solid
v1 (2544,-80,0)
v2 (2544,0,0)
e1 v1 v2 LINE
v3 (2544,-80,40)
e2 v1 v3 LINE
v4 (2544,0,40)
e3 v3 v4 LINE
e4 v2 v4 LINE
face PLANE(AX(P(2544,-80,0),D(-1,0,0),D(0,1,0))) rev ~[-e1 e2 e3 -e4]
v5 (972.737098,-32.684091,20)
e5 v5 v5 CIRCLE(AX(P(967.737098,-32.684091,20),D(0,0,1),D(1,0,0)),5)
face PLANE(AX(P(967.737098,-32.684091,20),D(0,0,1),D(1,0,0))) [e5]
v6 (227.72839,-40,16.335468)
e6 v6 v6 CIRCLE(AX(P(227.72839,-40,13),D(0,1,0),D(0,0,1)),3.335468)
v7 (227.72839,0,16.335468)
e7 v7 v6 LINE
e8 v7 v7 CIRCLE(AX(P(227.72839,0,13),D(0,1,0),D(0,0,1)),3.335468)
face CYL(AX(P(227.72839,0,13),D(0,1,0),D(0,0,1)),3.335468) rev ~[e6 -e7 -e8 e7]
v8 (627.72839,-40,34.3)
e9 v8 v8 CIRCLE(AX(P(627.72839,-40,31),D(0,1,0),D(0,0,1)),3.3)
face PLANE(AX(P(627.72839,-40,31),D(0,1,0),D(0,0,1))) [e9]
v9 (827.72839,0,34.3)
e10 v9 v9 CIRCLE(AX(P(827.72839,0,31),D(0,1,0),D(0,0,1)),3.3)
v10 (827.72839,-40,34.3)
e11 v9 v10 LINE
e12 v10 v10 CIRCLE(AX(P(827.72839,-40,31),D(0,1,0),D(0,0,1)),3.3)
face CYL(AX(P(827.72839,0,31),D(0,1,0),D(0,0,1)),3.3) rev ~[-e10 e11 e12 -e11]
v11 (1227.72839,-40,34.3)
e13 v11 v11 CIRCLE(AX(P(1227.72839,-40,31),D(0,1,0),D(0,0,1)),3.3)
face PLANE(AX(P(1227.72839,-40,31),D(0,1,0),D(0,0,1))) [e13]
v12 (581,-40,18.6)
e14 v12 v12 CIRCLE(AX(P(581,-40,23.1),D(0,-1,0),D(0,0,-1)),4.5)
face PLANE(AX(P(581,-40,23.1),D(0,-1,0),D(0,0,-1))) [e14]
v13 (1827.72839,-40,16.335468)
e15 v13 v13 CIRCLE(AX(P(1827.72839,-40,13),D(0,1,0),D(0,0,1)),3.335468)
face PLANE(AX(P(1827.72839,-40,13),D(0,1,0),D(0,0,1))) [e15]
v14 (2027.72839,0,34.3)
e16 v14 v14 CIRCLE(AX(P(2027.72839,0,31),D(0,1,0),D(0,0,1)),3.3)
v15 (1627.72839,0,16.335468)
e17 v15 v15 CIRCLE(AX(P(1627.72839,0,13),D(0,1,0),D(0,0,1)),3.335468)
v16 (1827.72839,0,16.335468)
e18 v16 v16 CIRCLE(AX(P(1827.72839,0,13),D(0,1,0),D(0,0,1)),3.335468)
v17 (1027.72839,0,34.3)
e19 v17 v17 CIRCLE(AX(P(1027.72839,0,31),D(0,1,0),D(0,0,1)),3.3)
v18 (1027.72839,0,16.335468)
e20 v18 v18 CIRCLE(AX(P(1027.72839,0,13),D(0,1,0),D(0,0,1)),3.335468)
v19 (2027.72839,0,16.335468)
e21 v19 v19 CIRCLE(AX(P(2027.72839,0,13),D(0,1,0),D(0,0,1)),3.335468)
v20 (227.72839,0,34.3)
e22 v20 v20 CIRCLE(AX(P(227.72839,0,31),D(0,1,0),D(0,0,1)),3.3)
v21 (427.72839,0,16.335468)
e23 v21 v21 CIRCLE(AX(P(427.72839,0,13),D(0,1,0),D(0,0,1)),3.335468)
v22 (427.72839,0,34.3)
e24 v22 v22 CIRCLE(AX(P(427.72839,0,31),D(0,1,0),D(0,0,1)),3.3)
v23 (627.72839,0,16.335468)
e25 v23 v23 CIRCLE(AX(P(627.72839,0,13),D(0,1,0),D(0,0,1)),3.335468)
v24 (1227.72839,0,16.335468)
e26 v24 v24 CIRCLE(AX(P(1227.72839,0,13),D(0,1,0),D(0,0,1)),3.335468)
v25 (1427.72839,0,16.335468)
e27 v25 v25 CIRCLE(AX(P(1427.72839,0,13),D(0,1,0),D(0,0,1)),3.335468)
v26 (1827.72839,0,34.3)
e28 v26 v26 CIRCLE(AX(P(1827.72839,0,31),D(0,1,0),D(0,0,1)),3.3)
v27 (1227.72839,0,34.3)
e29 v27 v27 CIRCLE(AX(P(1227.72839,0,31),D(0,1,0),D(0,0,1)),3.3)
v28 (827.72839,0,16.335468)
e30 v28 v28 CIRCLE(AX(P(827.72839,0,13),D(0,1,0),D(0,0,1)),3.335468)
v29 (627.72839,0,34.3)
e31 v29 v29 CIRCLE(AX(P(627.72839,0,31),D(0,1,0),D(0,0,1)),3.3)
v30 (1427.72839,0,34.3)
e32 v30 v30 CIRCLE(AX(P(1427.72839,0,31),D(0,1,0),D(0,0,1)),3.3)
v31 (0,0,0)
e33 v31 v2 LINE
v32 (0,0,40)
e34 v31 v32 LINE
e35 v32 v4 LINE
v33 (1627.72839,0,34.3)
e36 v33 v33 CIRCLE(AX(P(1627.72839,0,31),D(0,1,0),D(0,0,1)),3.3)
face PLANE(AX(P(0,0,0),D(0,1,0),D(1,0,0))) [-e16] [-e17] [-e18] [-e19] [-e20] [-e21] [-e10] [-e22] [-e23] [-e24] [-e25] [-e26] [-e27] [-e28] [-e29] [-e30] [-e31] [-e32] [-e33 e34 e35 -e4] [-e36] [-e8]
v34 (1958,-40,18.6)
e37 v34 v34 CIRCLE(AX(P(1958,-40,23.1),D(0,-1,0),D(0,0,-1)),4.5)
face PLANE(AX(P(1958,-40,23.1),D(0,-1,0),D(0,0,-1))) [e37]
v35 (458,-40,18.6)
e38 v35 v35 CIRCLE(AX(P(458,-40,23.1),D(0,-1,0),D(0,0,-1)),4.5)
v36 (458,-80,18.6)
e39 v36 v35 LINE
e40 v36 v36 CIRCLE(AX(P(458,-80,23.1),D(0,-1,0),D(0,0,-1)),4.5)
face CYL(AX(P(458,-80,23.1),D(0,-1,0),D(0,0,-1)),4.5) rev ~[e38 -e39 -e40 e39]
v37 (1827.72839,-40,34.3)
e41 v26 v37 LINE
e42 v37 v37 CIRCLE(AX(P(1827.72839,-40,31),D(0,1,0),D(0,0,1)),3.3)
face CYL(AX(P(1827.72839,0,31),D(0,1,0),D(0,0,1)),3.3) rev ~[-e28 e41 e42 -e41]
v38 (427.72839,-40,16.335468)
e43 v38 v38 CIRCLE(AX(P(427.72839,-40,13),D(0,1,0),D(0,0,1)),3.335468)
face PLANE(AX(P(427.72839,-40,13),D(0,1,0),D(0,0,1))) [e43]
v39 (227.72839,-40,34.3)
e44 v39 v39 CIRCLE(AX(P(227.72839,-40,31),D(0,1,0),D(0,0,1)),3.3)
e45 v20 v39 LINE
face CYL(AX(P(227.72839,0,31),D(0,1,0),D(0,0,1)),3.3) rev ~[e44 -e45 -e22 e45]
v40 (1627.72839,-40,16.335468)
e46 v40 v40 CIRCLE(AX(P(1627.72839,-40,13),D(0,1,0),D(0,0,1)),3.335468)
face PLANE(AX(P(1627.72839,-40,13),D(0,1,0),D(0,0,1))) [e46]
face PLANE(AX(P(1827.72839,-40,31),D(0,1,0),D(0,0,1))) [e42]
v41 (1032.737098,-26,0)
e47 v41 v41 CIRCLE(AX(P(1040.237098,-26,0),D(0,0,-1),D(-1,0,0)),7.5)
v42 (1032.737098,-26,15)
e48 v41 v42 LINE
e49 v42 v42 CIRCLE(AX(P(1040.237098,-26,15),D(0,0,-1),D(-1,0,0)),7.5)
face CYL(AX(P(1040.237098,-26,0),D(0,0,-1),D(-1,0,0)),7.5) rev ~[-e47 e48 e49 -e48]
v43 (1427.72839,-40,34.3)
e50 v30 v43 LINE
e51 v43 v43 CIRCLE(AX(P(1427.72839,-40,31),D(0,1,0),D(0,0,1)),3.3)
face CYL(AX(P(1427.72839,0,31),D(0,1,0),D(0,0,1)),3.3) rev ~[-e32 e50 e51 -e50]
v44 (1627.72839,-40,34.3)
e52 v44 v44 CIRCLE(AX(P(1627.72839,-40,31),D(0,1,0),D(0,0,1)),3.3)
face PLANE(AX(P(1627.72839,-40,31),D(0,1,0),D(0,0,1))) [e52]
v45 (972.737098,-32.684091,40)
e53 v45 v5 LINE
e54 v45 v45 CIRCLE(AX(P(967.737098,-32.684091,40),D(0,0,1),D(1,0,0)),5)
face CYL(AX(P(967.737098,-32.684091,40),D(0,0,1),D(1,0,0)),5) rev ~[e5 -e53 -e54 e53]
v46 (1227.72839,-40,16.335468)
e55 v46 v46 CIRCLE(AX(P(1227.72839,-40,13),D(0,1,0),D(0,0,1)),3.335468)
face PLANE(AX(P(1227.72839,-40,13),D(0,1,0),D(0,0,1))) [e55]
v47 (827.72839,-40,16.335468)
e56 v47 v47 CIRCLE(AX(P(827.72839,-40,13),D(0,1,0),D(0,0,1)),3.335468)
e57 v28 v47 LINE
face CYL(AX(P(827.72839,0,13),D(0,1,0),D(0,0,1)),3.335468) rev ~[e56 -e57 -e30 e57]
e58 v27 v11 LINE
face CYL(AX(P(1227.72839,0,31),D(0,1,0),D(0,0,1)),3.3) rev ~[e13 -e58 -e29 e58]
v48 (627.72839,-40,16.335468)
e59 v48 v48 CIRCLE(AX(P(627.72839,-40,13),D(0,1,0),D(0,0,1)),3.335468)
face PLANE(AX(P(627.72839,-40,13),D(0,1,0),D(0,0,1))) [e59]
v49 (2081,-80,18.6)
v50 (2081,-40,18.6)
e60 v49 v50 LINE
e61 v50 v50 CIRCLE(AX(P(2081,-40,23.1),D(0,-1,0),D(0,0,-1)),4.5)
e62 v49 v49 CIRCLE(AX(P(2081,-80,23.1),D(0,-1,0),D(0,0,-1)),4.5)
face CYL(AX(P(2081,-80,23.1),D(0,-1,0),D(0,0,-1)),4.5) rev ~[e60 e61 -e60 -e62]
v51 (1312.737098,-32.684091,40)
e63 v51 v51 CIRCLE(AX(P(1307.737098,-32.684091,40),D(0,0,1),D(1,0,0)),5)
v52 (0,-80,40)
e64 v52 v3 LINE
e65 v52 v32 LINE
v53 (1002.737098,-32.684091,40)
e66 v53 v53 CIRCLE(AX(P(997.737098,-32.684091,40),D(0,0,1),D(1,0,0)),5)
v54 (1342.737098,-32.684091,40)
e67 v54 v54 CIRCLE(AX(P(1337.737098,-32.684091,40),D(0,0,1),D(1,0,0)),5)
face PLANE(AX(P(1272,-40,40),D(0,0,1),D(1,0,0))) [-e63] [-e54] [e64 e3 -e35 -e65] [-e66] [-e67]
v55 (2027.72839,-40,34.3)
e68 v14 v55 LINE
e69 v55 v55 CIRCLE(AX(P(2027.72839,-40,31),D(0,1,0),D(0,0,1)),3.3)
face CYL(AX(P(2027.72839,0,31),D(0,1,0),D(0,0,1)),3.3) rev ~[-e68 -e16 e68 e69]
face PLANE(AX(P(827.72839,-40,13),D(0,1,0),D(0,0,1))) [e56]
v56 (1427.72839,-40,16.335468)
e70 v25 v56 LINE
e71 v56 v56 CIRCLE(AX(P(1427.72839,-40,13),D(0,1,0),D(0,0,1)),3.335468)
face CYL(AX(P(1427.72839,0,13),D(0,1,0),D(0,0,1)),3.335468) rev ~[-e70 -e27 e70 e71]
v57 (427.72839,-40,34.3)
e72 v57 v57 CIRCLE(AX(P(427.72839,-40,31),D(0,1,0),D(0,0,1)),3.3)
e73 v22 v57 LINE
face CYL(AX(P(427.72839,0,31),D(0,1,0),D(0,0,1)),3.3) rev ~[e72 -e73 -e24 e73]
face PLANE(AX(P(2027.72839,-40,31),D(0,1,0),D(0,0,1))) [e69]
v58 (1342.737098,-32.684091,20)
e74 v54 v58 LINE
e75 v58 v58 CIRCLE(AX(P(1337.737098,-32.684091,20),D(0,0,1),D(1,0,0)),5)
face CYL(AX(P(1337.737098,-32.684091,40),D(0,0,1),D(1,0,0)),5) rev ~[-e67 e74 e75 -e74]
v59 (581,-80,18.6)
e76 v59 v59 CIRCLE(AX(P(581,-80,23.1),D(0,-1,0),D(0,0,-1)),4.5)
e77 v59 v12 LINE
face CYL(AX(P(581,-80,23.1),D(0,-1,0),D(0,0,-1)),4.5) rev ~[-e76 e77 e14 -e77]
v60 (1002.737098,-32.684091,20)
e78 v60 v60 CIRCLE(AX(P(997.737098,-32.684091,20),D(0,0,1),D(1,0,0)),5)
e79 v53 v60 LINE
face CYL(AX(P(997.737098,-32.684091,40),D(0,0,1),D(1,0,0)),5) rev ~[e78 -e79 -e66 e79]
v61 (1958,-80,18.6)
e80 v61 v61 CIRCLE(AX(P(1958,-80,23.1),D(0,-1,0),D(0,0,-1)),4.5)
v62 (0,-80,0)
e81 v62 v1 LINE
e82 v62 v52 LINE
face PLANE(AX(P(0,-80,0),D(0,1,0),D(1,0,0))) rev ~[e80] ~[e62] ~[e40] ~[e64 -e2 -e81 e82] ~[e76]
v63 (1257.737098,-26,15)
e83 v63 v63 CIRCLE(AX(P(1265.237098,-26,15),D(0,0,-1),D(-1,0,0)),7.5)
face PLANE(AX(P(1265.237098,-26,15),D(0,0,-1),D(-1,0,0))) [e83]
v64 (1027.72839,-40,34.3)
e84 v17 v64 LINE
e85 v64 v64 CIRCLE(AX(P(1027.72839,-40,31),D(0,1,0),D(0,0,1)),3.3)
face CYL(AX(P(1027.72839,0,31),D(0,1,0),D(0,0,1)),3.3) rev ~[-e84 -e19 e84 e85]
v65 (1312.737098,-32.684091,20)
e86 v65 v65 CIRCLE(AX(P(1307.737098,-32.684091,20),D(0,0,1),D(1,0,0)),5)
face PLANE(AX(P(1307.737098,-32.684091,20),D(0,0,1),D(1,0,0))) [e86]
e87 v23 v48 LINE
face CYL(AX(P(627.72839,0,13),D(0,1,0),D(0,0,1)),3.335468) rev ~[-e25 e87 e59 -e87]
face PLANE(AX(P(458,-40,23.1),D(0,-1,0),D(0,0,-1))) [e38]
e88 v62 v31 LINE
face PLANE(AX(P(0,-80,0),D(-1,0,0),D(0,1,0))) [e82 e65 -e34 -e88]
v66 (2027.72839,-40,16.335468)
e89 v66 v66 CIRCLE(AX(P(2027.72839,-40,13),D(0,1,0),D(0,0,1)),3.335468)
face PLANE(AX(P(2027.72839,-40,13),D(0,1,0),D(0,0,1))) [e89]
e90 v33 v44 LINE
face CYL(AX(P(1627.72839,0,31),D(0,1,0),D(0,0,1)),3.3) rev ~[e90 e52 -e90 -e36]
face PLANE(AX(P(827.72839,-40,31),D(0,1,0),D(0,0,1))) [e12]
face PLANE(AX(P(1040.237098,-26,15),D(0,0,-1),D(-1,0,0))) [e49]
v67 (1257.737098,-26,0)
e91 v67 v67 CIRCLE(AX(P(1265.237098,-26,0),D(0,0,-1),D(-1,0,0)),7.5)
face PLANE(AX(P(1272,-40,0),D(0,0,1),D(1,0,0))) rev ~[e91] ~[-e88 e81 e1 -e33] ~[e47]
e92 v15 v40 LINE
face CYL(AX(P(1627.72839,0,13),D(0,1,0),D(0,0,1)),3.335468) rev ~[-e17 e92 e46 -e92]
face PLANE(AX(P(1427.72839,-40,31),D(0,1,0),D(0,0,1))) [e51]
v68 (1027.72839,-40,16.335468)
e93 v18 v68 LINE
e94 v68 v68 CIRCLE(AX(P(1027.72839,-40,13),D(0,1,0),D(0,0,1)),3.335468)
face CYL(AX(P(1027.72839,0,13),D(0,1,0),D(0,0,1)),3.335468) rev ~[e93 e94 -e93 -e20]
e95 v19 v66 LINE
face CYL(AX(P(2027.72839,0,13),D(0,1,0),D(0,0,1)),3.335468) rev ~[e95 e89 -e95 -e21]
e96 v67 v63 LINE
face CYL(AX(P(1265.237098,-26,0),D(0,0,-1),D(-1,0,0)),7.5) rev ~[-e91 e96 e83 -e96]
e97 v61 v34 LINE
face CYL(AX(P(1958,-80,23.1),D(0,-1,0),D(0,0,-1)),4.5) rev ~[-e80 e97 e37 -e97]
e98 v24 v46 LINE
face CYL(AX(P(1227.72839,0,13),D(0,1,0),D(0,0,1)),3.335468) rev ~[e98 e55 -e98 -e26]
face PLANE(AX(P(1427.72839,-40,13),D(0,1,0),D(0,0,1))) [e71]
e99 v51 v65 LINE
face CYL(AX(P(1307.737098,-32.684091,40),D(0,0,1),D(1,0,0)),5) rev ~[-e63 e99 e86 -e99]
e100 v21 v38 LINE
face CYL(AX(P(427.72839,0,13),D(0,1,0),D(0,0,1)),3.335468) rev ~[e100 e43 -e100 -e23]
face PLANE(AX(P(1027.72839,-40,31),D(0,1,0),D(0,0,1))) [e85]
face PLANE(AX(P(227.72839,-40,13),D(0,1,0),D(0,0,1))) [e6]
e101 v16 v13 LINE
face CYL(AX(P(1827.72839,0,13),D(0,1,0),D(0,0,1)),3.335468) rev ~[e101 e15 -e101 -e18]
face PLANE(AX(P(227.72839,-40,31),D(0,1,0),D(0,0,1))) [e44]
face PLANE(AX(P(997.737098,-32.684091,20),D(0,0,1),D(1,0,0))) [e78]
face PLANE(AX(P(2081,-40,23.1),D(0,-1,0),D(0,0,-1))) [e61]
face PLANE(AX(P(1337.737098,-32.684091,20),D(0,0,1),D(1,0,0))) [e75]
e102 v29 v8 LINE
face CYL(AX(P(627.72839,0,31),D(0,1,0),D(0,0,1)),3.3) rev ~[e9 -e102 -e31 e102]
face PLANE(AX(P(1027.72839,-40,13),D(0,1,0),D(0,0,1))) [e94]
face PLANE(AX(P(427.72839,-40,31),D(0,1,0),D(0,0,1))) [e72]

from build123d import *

# Parameters (mm, degrees)
SKETCH_1_W             = 2544
SKETCH_1_H             = 80
EXTRUDE_1_DEPTH        = 40
SKETCH_2_R             = 3.335467959
SKETCH_2_R_2           = 3.3
CUT_EXTRUDE_1_DEPTH    = 40
PATTERN_LINEAR_1_COUNT = 10
PATTERN_LINEAR_1_PITCH = 200
SKETCH_3_R             = 4.5
CUT_EXTRUDE_2_DEPTH    = 40
SKETCH_4_R             = 5
CUT_EXTRUDE_3_DEPTH    = 20
SKETCH_5_R             = 7.5
CUT_EXTRUDE_4_DEPTH    = 15


with BuildPart() as part:
    # 草图1 → 凸台-拉伸1 (new body)
    with BuildSketch(Plane.XY):
        with Locations((1272, -40)):
            Rectangle(SKETCH_1_W, SKETCH_1_H)
    extrude(amount=EXTRUDE_1_DEPTH)

    # 草图2 → 切除-拉伸1 (cut)
    with BuildSketch(Plane(origin=(0, 0, 0), x_dir=(1, 0, 0), z_dir=(0, 1, 0))):
        with Locations(Location((227.728390154, -13, 0), (0, 0, 270))):
            Circle(SKETCH_2_R)
        with Locations(Location((227.728390154, -31, 0), (0, 0, 270))):
            Circle(SKETCH_2_R_2)
    cut_extrude_1 = extrude(amount=-CUT_EXTRUDE_1_DEPTH, mode=Mode.SUBTRACT)

    # 阵列(线性)1: 切除-拉伸1 ×10
    with Locations(*[(i * PATTERN_LINEAR_1_PITCH, 0, 0) for i in range(1, PATTERN_LINEAR_1_COUNT)]):
        add(cut_extrude_1, mode=Mode.SUBTRACT)

    # 草图3 → 切除-拉伸2 (cut)
    with BuildSketch(Plane.XZ.offset(80)):
        with Locations(Location((458, 23.1, 0), (0, 0, 270))):
            Circle(SKETCH_3_R)
        with Locations(Location((581, 23.1, 0), (0, 0, 270))):
            Circle(SKETCH_3_R)
        with Locations(Location((1958, 23.1, 0), (0, 0, 270))):
            Circle(SKETCH_3_R)
        with Locations(Location((2081, 23.1, 0), (0, 0, 270))):
            Circle(SKETCH_3_R)
    extrude(amount=-CUT_EXTRUDE_2_DEPTH, mode=Mode.SUBTRACT)

    # 草图4 → 切除-拉伸3 (cut)
    with BuildSketch(Plane.XY.offset(40)):
        with Locations((1337.7370976, -32.684091126)):
            Circle(SKETCH_4_R)
        with Locations((1307.7370976, -32.684091126)):
            Circle(SKETCH_4_R)
        with Locations((997.7370976, -32.684091126)):
            Circle(SKETCH_4_R)
        with Locations((967.7370976, -32.684091126)):
            Circle(SKETCH_4_R)
    extrude(amount=-CUT_EXTRUDE_3_DEPTH, mode=Mode.SUBTRACT)

    # 草图5 → 切除-拉伸4 (cut)
    with BuildSketch(Plane(origin=(0, 0, 0), x_dir=(-1, 0, 0), z_dir=(0, 0, -1))):
        with Locations((-1265.2370976, -26)):
            Circle(SKETCH_5_R)
        with Locations((-1040.2370976, -26)):
            Circle(SKETCH_5_R)
    extrude(amount=-CUT_EXTRUDE_4_DEPTH, mode=Mode.SUBTRACT)


solid = part.part
